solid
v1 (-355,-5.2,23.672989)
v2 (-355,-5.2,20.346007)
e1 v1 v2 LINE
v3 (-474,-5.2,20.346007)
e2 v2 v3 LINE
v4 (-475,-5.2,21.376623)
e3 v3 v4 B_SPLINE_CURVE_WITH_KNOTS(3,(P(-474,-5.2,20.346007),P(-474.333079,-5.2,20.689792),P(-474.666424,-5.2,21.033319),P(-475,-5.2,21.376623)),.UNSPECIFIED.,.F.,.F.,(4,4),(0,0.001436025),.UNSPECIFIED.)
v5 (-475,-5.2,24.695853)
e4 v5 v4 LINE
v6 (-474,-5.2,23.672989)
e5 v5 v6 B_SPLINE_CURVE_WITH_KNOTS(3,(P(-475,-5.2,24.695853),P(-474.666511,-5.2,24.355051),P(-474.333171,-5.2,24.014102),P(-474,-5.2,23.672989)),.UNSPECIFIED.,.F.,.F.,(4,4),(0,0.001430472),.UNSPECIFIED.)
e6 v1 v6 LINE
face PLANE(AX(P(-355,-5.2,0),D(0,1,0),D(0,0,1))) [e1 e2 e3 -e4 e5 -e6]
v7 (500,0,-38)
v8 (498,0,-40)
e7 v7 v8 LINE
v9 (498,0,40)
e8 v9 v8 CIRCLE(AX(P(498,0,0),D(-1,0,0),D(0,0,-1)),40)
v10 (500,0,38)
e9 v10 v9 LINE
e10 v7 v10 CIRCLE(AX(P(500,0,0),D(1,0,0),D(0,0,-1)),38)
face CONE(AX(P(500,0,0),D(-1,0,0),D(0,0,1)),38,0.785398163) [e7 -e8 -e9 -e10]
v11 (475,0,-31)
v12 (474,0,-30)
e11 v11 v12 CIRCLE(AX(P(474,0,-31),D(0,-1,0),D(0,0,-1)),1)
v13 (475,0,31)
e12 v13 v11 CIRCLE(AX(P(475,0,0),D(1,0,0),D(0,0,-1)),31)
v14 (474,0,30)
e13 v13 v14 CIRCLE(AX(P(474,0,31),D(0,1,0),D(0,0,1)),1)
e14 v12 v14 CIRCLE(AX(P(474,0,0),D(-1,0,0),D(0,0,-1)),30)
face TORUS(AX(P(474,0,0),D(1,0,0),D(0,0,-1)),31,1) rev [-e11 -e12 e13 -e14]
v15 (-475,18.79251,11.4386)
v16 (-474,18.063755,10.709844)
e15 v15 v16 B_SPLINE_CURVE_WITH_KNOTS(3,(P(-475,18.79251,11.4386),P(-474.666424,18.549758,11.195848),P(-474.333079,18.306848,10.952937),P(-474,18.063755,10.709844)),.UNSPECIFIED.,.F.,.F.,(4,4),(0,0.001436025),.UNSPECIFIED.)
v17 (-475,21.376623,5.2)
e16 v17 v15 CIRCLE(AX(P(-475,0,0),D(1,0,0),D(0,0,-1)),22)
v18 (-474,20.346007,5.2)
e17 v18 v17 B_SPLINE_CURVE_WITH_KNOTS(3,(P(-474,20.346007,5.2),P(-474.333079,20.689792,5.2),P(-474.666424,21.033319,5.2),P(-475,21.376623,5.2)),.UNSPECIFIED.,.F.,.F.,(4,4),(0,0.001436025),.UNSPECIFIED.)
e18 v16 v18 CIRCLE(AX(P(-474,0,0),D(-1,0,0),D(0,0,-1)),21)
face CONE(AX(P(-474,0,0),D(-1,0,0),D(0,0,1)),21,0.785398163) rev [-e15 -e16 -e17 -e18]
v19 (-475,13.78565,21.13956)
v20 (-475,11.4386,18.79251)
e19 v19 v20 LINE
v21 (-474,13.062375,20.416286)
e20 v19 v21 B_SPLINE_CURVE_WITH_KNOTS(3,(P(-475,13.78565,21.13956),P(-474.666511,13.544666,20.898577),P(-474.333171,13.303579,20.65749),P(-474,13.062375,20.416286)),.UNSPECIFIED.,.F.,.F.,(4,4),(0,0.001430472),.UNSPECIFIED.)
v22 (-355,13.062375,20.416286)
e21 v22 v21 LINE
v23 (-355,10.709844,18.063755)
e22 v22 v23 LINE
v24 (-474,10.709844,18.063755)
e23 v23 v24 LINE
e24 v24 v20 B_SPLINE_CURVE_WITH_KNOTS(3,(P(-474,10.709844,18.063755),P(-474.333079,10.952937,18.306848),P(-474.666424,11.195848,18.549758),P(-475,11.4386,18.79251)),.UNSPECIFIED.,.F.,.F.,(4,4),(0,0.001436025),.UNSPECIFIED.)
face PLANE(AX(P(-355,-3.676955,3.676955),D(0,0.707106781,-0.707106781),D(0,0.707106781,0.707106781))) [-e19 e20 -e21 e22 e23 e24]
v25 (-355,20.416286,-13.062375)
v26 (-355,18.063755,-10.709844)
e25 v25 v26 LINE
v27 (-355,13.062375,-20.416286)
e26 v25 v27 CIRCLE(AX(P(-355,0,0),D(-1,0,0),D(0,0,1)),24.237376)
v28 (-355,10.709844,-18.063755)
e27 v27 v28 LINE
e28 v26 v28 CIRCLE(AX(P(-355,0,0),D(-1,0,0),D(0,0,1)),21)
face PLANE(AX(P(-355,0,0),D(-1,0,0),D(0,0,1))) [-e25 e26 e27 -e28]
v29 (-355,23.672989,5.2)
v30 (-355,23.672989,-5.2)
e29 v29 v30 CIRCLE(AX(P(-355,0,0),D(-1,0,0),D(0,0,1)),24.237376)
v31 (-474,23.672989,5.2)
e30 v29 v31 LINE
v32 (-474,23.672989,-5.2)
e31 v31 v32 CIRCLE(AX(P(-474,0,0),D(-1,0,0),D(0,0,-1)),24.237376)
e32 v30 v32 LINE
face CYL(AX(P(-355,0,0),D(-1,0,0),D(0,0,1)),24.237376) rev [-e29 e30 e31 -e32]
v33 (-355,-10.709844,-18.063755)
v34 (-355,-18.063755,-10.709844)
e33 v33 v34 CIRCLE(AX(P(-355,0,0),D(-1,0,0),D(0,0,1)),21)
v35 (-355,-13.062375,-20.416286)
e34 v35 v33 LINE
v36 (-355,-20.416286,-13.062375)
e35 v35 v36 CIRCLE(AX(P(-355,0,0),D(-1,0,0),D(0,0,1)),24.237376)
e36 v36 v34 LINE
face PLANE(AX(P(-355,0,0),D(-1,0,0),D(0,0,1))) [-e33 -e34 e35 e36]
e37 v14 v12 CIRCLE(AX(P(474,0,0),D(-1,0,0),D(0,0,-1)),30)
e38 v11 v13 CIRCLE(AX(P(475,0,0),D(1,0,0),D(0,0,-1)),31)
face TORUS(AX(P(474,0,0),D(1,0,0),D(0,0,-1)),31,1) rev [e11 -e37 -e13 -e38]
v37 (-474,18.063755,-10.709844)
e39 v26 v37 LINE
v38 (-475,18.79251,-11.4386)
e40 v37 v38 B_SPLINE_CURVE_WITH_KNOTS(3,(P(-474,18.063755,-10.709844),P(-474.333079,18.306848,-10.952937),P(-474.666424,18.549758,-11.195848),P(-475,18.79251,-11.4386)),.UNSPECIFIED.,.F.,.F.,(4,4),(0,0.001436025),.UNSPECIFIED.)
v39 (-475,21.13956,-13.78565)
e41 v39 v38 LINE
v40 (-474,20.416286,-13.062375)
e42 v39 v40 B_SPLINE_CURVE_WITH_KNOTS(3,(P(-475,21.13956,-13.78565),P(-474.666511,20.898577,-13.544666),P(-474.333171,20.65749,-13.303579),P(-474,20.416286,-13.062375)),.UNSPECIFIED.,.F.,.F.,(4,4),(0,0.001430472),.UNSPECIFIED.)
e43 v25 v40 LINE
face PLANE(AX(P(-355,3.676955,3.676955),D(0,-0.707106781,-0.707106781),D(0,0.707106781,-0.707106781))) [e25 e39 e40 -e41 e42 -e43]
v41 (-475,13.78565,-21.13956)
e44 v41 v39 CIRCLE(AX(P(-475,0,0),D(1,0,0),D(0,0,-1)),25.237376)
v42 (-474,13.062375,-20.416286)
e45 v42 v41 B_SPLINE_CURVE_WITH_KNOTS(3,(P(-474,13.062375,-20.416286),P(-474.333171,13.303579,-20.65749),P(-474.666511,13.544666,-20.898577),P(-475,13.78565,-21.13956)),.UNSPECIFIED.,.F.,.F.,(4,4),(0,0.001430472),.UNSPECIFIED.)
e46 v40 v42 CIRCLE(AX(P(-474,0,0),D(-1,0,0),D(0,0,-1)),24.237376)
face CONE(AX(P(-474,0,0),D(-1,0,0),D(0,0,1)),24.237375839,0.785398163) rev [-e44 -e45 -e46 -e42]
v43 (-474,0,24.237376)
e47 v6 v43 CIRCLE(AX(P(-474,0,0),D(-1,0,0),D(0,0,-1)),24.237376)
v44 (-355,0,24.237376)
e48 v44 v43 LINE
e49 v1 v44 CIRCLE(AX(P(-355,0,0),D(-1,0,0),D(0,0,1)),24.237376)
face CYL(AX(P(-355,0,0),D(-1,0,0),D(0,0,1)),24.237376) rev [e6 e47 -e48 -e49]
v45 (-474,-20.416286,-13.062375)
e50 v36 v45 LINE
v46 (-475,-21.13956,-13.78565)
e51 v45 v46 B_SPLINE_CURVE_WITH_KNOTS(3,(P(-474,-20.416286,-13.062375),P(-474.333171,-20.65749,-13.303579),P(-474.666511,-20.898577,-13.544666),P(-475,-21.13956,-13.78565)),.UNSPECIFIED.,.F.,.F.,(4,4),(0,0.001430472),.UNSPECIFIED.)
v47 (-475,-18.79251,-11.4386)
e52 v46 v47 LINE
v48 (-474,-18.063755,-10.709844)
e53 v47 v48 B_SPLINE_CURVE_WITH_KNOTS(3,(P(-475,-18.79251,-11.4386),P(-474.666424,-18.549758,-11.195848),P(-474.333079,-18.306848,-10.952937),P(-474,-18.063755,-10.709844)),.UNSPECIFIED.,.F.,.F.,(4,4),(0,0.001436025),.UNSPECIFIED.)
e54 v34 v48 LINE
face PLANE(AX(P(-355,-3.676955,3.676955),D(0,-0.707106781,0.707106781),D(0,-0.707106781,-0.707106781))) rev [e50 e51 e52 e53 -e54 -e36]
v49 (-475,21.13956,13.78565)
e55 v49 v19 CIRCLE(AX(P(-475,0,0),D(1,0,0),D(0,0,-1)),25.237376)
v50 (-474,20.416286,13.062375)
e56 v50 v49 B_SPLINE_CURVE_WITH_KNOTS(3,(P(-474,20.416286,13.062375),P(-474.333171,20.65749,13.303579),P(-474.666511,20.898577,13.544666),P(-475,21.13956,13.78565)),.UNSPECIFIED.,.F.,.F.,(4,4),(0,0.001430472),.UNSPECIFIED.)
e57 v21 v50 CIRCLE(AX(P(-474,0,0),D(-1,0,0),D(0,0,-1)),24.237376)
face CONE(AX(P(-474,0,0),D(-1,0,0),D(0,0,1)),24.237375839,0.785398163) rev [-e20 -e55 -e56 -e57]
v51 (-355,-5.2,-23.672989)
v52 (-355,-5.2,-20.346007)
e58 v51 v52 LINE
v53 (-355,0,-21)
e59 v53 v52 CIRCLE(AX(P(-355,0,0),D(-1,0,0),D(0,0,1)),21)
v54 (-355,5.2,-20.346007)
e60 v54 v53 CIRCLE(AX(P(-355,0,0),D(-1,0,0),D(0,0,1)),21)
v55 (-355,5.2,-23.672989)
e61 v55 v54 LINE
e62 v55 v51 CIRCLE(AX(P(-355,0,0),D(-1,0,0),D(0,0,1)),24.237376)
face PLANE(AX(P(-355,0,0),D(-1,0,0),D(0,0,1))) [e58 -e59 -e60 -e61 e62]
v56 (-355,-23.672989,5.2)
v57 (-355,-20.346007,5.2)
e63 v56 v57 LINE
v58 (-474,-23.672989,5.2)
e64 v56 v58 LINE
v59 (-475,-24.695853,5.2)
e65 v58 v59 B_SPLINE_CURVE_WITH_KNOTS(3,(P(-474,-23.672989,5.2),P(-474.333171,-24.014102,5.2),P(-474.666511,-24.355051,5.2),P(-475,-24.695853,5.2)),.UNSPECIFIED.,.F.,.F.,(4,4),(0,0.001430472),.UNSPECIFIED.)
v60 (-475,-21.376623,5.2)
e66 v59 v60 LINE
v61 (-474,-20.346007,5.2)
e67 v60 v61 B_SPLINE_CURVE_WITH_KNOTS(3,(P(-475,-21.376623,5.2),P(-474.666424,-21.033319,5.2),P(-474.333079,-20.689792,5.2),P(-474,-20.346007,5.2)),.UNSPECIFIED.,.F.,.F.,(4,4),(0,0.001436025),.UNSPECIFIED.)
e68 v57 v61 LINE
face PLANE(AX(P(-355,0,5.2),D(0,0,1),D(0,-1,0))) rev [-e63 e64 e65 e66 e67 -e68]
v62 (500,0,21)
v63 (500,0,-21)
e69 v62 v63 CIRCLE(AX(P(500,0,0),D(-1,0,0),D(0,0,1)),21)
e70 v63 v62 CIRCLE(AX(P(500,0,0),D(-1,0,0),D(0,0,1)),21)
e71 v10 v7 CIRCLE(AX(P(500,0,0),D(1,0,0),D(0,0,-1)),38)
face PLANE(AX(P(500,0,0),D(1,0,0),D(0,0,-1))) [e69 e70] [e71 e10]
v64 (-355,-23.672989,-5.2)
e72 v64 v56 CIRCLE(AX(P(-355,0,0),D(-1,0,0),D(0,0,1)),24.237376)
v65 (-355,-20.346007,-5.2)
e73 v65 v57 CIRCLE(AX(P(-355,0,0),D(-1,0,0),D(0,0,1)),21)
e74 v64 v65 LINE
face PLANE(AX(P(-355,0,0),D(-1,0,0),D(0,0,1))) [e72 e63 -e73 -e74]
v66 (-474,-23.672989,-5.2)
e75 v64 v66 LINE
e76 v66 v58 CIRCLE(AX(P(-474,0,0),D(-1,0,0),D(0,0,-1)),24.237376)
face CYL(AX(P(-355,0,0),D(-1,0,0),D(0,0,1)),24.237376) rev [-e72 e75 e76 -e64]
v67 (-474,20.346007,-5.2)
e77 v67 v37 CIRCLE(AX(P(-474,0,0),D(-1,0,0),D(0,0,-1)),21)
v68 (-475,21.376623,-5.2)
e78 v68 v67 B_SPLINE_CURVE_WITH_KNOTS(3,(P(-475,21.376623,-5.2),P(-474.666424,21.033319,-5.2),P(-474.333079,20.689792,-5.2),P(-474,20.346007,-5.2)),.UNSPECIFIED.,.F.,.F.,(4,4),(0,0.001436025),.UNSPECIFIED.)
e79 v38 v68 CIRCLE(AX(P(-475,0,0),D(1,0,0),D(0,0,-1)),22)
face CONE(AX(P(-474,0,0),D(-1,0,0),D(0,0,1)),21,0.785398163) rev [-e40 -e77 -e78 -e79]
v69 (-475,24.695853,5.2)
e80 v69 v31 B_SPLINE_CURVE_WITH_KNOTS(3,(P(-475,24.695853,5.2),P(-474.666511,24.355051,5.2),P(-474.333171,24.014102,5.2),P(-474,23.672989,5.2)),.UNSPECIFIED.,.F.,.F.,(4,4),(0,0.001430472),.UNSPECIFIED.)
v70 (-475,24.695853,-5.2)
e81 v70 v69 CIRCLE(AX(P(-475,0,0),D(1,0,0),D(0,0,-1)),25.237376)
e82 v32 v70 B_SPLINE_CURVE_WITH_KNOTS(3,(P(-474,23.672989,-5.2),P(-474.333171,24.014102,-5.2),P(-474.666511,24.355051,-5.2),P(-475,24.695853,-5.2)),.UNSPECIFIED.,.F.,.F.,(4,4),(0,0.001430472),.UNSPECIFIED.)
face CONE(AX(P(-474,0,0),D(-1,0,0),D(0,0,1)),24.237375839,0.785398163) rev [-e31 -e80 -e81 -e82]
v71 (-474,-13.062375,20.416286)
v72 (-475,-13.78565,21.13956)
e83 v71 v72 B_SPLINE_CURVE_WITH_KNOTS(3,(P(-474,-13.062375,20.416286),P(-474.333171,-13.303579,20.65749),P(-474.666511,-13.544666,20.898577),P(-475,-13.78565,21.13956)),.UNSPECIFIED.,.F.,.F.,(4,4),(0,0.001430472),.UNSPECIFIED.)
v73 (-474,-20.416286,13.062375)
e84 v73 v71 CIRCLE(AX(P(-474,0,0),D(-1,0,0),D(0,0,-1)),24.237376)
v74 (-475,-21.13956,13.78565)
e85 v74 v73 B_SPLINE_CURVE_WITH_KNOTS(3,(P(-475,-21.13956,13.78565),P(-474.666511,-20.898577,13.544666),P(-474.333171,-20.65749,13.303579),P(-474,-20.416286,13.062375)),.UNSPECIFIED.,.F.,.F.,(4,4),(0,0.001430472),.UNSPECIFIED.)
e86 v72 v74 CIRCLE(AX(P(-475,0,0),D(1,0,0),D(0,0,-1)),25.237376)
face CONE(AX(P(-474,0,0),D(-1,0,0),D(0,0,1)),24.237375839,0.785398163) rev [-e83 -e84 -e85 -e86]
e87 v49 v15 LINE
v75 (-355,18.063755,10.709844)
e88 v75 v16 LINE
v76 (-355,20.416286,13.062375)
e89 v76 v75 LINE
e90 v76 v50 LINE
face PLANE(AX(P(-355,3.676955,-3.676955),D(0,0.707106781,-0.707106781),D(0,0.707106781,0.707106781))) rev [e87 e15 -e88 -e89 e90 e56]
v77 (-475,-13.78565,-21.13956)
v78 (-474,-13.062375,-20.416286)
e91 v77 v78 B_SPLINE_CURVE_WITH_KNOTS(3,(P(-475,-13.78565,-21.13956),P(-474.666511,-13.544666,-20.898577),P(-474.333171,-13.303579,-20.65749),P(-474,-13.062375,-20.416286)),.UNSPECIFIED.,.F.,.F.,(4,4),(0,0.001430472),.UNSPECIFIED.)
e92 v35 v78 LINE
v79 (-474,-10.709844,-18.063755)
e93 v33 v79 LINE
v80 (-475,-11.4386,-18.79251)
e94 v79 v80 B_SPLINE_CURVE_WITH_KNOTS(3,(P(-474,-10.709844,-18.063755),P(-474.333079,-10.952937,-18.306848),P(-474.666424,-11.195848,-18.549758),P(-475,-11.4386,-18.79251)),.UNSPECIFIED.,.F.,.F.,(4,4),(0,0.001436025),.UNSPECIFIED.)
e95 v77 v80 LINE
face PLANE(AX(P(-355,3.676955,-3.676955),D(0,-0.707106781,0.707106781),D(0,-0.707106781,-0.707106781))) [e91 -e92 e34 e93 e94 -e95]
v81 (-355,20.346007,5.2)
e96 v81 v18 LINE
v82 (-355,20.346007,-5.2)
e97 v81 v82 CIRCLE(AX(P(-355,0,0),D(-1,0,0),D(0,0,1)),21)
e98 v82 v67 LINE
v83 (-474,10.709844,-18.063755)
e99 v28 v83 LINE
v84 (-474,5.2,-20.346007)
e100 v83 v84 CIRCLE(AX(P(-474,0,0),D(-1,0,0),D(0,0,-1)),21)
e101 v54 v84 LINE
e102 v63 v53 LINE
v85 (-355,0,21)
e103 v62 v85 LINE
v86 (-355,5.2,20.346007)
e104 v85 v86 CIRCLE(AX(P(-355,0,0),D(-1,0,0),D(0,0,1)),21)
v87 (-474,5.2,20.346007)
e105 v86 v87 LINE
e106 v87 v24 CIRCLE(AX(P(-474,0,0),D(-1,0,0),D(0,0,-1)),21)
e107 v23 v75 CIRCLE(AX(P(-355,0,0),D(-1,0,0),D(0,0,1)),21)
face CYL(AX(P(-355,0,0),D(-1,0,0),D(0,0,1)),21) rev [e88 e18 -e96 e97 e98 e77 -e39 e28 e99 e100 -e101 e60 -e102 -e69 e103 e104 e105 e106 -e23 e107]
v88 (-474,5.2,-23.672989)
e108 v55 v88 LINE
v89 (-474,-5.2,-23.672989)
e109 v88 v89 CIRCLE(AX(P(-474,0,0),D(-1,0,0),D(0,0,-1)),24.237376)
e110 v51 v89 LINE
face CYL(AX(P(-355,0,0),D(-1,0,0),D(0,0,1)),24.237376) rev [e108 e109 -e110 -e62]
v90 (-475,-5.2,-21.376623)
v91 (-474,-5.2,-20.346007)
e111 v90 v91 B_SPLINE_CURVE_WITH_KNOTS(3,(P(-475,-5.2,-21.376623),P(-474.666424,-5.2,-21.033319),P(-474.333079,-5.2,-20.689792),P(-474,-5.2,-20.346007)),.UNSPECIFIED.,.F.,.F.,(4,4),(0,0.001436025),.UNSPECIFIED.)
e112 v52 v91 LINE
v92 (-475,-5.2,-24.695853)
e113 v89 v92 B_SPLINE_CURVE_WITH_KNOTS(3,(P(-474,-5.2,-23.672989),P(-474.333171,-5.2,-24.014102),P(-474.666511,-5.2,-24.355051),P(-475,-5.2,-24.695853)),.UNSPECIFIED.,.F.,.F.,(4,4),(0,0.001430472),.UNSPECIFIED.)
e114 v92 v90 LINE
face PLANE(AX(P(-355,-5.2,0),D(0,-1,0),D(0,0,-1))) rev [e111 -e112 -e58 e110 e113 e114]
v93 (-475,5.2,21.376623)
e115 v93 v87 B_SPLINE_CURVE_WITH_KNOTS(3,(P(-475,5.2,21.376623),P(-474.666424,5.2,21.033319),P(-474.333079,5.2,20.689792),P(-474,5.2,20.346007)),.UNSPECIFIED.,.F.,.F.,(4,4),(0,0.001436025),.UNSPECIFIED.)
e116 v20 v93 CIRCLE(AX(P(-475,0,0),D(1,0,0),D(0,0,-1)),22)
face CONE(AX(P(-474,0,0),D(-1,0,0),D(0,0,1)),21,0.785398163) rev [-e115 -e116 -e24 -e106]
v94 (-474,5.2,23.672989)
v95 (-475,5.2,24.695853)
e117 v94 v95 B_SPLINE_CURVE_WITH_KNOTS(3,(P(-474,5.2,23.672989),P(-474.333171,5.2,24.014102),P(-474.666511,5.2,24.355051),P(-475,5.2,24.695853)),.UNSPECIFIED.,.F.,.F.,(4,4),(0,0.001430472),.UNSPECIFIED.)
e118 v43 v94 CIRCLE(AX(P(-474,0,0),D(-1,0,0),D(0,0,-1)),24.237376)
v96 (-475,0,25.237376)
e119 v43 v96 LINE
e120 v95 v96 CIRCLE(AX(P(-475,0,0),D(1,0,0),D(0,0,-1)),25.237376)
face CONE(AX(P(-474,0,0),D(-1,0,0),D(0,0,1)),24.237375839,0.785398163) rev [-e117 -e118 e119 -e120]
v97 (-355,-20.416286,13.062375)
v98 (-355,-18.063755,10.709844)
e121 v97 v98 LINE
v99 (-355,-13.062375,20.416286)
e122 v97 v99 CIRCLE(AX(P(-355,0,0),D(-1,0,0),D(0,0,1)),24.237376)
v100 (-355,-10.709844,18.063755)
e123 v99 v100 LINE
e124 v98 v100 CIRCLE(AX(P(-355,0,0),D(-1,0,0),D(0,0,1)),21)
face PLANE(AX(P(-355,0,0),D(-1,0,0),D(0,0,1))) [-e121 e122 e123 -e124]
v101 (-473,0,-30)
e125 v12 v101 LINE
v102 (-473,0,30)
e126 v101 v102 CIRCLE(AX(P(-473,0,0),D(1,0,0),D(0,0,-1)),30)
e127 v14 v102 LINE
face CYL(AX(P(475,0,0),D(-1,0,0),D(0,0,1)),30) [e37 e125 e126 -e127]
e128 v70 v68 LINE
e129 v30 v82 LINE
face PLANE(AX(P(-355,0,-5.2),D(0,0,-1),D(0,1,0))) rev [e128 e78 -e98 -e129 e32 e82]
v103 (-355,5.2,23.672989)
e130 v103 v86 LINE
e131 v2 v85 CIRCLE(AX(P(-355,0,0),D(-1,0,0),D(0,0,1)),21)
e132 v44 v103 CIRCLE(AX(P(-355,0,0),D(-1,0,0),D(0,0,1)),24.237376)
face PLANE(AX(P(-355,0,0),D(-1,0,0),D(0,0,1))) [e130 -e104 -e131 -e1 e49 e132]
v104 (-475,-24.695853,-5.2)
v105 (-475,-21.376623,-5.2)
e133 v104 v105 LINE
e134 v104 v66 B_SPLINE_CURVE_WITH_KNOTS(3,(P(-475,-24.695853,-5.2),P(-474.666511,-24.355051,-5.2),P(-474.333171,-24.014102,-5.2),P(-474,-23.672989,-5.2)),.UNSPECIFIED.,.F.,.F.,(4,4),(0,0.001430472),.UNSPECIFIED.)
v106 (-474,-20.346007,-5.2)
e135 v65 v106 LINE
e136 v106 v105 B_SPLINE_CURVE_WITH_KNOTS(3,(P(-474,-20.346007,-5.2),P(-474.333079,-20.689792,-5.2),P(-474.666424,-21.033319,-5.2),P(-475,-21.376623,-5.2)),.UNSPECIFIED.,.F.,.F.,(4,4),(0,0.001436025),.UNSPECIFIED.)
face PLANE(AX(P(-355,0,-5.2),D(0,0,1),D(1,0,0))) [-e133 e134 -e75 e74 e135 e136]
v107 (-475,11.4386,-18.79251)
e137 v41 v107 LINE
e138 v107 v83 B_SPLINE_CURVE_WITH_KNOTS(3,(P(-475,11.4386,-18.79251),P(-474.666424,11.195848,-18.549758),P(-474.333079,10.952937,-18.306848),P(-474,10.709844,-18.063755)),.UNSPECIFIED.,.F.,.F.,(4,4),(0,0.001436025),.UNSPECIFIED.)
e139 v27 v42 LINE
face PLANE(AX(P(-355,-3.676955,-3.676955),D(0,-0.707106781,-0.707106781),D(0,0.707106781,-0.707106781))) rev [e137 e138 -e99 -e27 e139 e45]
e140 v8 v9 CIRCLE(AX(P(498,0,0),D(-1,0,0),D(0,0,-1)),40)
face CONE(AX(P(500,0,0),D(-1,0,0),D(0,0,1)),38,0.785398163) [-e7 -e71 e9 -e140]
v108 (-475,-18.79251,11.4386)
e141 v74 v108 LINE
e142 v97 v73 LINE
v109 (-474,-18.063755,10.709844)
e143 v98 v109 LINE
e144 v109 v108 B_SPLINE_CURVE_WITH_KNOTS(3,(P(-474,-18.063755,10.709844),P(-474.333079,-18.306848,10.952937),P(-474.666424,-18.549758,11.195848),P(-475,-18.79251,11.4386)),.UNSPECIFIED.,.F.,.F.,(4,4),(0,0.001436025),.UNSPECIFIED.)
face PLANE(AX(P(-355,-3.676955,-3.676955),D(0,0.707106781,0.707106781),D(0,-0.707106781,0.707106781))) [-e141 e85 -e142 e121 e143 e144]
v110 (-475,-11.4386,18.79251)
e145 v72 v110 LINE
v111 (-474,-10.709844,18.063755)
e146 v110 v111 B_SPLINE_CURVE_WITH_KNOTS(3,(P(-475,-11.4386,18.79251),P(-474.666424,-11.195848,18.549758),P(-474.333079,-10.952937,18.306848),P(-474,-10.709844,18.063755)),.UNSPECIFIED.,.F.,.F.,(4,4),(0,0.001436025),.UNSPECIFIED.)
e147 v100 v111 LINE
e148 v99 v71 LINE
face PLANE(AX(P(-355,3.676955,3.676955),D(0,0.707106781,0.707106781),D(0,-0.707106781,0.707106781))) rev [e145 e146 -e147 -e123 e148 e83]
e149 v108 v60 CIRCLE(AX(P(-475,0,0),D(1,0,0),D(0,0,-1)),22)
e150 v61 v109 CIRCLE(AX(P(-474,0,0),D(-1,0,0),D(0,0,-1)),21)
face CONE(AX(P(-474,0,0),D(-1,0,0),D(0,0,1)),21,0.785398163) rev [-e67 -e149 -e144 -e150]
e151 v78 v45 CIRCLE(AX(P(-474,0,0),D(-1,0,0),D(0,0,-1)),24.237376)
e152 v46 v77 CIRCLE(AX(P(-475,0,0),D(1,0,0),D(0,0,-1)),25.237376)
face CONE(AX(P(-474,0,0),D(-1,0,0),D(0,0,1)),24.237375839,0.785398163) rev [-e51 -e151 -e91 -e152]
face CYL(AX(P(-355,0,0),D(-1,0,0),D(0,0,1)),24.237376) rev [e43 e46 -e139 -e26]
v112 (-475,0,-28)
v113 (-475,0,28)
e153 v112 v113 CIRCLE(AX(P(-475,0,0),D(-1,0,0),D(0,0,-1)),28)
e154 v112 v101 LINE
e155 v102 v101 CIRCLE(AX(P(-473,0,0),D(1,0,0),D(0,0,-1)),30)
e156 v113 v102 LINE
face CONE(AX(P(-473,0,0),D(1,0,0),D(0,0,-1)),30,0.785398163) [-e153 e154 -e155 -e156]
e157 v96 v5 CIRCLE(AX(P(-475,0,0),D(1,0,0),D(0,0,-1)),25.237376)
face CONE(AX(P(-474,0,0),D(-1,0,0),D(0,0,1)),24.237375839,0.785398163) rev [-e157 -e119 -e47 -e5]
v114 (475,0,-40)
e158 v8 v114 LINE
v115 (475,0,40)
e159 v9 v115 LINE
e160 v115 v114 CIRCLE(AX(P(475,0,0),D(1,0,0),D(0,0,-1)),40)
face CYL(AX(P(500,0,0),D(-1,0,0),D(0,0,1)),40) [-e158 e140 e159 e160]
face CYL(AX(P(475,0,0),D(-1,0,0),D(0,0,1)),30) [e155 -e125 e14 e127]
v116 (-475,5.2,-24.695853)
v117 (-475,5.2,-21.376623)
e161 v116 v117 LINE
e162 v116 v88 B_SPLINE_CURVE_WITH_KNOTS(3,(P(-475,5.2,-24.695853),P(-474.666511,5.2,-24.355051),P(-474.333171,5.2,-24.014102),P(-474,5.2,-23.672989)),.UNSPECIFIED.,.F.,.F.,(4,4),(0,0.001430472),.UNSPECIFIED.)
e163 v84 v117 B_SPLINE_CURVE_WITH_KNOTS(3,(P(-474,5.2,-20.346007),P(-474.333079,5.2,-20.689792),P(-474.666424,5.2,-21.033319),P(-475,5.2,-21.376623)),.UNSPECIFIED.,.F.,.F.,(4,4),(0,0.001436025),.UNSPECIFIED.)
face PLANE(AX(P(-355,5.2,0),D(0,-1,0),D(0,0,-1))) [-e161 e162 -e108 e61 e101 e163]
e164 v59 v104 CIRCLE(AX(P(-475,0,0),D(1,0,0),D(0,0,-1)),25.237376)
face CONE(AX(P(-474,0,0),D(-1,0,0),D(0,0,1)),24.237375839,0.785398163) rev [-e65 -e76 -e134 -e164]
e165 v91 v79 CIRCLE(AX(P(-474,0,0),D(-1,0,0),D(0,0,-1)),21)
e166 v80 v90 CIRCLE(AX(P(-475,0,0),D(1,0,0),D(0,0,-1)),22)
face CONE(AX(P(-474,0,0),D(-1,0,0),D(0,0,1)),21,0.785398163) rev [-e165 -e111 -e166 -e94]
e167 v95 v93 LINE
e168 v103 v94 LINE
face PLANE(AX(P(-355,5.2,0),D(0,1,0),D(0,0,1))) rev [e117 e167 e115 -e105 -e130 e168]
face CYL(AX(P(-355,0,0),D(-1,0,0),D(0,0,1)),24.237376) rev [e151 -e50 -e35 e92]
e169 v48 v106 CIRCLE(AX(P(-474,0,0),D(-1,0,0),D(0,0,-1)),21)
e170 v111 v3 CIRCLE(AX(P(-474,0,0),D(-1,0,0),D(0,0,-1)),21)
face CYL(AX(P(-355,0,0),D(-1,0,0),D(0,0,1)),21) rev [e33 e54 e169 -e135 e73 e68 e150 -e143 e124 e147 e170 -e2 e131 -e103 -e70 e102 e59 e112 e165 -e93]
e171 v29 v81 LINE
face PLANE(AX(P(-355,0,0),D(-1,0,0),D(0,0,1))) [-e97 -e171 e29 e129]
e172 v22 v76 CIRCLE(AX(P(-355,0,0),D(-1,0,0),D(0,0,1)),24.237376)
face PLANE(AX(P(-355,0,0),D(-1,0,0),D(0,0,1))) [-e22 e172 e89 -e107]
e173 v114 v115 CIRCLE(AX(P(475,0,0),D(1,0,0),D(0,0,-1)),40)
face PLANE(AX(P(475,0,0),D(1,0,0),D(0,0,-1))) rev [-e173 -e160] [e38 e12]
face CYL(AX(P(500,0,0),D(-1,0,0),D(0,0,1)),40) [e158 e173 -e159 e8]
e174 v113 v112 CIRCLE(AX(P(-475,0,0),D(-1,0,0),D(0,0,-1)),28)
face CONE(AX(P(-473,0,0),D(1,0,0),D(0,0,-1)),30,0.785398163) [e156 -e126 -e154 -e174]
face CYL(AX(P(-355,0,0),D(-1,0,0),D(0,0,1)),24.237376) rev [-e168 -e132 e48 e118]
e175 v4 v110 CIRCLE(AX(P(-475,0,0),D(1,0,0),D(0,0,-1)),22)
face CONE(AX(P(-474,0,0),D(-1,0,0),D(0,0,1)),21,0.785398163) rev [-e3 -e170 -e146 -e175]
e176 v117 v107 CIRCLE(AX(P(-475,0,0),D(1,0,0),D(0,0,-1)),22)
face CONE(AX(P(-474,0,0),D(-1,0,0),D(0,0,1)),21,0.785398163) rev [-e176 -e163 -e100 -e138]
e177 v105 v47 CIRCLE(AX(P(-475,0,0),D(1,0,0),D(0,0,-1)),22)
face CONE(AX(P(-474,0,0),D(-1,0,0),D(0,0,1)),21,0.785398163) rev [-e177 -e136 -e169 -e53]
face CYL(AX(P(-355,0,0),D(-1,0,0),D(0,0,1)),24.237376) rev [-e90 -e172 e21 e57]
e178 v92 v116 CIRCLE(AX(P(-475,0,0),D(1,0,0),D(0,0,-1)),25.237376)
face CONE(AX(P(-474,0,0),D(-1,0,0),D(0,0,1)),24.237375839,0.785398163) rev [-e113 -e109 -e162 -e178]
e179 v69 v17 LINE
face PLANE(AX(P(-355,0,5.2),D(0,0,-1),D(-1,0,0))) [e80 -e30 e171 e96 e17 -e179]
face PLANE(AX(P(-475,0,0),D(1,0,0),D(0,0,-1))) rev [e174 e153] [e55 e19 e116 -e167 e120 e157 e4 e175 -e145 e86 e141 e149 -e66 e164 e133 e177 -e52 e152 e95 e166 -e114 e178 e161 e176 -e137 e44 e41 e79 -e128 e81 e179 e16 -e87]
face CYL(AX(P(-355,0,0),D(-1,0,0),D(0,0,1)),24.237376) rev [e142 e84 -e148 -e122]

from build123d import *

# Parameters (mm, degrees)
SKETCH_1_R          = 30
EXTRUDE_1_DEPTH     = 475
SKETCH_2_R          = 40
EXTRUDE_2_DEPTH     = 25
CHAMFER_1_SIZE      = 2
FILLET_1_R          = 1
CUT_EXTRUDE_2_DEPTH = 120
SKETCH_5_R          = 21
CUT_EXTRUDE_3_DEPTH = 857.869301586
CHAMFER_2_SIZE      = 2
CHAMFER_3_SIZE      = 1


with BuildPart() as part:
    # 草图1 → 凸台-拉伸1 (new, symmetric)
    with BuildSketch(Plane(origin=(0, 0, 0), x_dir=(0, 0, -1), z_dir=(1, 0, 0))):
        with Locations(Location((0, 0, 0), (0, 0, 180))):
            Circle(SKETCH_1_R)
    extrude(amount=EXTRUDE_1_DEPTH, both=True)

    # 草图2 → 凸台-拉伸2 (add)
    with BuildSketch(Plane(origin=(475, 0, 0), x_dir=(0, 0, -1), z_dir=(1, 0, 0))):
        Circle(SKETCH_2_R)
    extrude(amount=EXTRUDE_2_DEPTH)

    # 倒角1
    chamfer_1_edges = [part.edges().sort_by_distance(p)[0] for p in [
        (500, 0, 40),
    ]]
    chamfer(chamfer_1_edges, length=CHAMFER_1_SIZE)

    # 圆角1
    fillet_1_edges = [part.edges().sort_by_distance(p)[0] for p in [
        (475, 0, -30),
    ]]
    fillet(fillet_1_edges, radius=FILLET_1_R)

    # 草图3 → 切除-拉伸2 (cut)
    with BuildSketch(Plane.ZY.offset(475)):
        with BuildLine():
            Line((0, -24.237375839), (0, 24.237375839))
            ThreePointArc((0, 24.237375839), (-2.61526925, 24.095865917), (-5.2, 23.672988564))
            Line((-5.2, 23.672988564), (-5.2, 20.346006979))
            ThreePointArc((-5.2, 20.346006979), (-8.03635208, 19.401470183), (-10.709844243, 18.063754767))
            Line((-10.709844243, 18.063754767), (-13.062375482, 20.416286007))
            ThreePointArc((-13.062375482, 20.416286007), (-17.138412814, 17.138412814), (-20.416286007, 13.062375482))
            Line((-20.416286007, 13.062375482), (-18.063754767, 10.709844243))
            ThreePointArc((-18.063754767, 10.709844243), (-19.401470183, 8.03635208), (-20.346006979, 5.2))
            Line((-20.346006979, 5.2), (-23.672988564, 5.2))
            ThreePointArc((-23.672988564, 5.2), (-24.237375839, 0), (-23.672988564, -5.2))
            Line((-23.672988564, -5.2), (-20.346006979, -5.2))
            ThreePointArc((-20.346006979, -5.2), (-19.401470183, -8.03635208), (-18.063754767, -10.709844243))
            Line((-18.063754767, -10.709844243), (-20.416286007, -13.062375482))
            ThreePointArc((-20.416286007, -13.062375482), (-17.138412814, -17.138412814), (-13.062375482, -20.416286007))
            Line((-13.062375482, -20.416286007), (-10.709844243, -18.063754767))
            ThreePointArc((-10.709844243, -18.063754767), (-8.03635208, -19.401470183), (-5.2, -20.346006979))
            Line((-5.2, -20.346006979), (-5.2, -23.672988564))
            ThreePointArc((-5.2, -23.672988564), (-2.61526925, -24.095865917), (0, -24.237375839))
        make_face()
        with BuildLine():
            ThreePointArc((5.2, 23.672988564), (2.61526925, 24.095865917), (0, 24.237375839))
            Line((0, 24.237375839), (0, -24.237375839))
            ThreePointArc((0, -24.237375839), (2.61526925, -24.095865917), (5.2, -23.672988564))
            Line((5.2, -23.672988564), (5.2, -20.346006979))
            ThreePointArc((5.2, -20.346006979), (8.03635208, -19.401470183), (10.709844243, -18.063754767))
            Line((10.709844243, -18.063754767), (13.062375482, -20.416286007))
            ThreePointArc((13.062375482, -20.416286007), (17.138412814, -17.138412814), (20.416286007, -13.062375482))
            Line((20.416286007, -13.062375482), (18.063754767, -10.709844243))
            ThreePointArc((18.063754767, -10.709844243), (19.401470183, -8.03635208), (20.346006979, -5.2))
            Line((20.346006979, -5.2), (23.672988564, -5.2))
            ThreePointArc((23.672988564, -5.2), (24.237375839, 0), (23.672988564, 5.2))
            Line((23.672988564, 5.2), (20.346006979, 5.2))
            ThreePointArc((20.346006979, 5.2), (19.401470183, 8.03635208), (18.063754767, 10.709844243))
            Line((18.063754767, 10.709844243), (20.416286007, 13.062375482))
            ThreePointArc((20.416286007, 13.062375482), (17.138412814, 17.138412814), (13.062375482, 20.416286007))
            Line((13.062375482, 20.416286007), (10.709844243, 18.063754767))
            ThreePointArc((10.709844243, 18.063754767), (8.03635208, 19.401470183), (5.2, 20.346006979))
            Line((5.2, 20.346006979), (5.2, 23.672988564))
        make_face()
    extrude(amount=-CUT_EXTRUDE_2_DEPTH, mode=Mode.SUBTRACT)

    # 草图5 → 切除-拉伸3 (cut, through all)
    with BuildSketch(Plane.ZY.offset(355)):
        Circle(SKETCH_5_R)
    extrude(amount=-CUT_EXTRUDE_3_DEPTH, mode=Mode.SUBTRACT)

    # 倒角2
    chamfer_2_edges = [part.edges().sort_by_distance(p)[0] for p in [
        (-475, 0, -30),
    ]]
    chamfer(chamfer_2_edges, length=CHAMFER_2_SIZE)

    # 倒角3
    chamfer_3_edges = [part.edges().sort_by_distance(p)[0] for p in [
        (-475, -24.237375839, 0),
        (-475, -19.401470183, 8.03635208),
        (-475, -17.138412814, 17.138412814),
        (-475, -8.03635208, 19.401470183),
        (-475, 0, 24.237375839),
        (-475, 8.03635208, 19.401470183),
        (-475, 17.138412814, 17.138412814),
        (-475, 19.401470183, 8.03635208),
        (-475, 24.237375839, 0),
        (-475, 19.401470183, -8.03635208),
        (-475, 17.138412814, -17.138412814),
        (-475, 8.03635208, -19.401470183),
        (-475, 0, -24.237375839),
        (-475, -8.03635208, -19.401470183),
        (-475, -17.138412814, -17.138412814),
        (-475, -19.401470183, -8.03635208),
    ]]
    chamfer(chamfer_3_edges, length=CHAMFER_3_SIZE)


solid = part.part
